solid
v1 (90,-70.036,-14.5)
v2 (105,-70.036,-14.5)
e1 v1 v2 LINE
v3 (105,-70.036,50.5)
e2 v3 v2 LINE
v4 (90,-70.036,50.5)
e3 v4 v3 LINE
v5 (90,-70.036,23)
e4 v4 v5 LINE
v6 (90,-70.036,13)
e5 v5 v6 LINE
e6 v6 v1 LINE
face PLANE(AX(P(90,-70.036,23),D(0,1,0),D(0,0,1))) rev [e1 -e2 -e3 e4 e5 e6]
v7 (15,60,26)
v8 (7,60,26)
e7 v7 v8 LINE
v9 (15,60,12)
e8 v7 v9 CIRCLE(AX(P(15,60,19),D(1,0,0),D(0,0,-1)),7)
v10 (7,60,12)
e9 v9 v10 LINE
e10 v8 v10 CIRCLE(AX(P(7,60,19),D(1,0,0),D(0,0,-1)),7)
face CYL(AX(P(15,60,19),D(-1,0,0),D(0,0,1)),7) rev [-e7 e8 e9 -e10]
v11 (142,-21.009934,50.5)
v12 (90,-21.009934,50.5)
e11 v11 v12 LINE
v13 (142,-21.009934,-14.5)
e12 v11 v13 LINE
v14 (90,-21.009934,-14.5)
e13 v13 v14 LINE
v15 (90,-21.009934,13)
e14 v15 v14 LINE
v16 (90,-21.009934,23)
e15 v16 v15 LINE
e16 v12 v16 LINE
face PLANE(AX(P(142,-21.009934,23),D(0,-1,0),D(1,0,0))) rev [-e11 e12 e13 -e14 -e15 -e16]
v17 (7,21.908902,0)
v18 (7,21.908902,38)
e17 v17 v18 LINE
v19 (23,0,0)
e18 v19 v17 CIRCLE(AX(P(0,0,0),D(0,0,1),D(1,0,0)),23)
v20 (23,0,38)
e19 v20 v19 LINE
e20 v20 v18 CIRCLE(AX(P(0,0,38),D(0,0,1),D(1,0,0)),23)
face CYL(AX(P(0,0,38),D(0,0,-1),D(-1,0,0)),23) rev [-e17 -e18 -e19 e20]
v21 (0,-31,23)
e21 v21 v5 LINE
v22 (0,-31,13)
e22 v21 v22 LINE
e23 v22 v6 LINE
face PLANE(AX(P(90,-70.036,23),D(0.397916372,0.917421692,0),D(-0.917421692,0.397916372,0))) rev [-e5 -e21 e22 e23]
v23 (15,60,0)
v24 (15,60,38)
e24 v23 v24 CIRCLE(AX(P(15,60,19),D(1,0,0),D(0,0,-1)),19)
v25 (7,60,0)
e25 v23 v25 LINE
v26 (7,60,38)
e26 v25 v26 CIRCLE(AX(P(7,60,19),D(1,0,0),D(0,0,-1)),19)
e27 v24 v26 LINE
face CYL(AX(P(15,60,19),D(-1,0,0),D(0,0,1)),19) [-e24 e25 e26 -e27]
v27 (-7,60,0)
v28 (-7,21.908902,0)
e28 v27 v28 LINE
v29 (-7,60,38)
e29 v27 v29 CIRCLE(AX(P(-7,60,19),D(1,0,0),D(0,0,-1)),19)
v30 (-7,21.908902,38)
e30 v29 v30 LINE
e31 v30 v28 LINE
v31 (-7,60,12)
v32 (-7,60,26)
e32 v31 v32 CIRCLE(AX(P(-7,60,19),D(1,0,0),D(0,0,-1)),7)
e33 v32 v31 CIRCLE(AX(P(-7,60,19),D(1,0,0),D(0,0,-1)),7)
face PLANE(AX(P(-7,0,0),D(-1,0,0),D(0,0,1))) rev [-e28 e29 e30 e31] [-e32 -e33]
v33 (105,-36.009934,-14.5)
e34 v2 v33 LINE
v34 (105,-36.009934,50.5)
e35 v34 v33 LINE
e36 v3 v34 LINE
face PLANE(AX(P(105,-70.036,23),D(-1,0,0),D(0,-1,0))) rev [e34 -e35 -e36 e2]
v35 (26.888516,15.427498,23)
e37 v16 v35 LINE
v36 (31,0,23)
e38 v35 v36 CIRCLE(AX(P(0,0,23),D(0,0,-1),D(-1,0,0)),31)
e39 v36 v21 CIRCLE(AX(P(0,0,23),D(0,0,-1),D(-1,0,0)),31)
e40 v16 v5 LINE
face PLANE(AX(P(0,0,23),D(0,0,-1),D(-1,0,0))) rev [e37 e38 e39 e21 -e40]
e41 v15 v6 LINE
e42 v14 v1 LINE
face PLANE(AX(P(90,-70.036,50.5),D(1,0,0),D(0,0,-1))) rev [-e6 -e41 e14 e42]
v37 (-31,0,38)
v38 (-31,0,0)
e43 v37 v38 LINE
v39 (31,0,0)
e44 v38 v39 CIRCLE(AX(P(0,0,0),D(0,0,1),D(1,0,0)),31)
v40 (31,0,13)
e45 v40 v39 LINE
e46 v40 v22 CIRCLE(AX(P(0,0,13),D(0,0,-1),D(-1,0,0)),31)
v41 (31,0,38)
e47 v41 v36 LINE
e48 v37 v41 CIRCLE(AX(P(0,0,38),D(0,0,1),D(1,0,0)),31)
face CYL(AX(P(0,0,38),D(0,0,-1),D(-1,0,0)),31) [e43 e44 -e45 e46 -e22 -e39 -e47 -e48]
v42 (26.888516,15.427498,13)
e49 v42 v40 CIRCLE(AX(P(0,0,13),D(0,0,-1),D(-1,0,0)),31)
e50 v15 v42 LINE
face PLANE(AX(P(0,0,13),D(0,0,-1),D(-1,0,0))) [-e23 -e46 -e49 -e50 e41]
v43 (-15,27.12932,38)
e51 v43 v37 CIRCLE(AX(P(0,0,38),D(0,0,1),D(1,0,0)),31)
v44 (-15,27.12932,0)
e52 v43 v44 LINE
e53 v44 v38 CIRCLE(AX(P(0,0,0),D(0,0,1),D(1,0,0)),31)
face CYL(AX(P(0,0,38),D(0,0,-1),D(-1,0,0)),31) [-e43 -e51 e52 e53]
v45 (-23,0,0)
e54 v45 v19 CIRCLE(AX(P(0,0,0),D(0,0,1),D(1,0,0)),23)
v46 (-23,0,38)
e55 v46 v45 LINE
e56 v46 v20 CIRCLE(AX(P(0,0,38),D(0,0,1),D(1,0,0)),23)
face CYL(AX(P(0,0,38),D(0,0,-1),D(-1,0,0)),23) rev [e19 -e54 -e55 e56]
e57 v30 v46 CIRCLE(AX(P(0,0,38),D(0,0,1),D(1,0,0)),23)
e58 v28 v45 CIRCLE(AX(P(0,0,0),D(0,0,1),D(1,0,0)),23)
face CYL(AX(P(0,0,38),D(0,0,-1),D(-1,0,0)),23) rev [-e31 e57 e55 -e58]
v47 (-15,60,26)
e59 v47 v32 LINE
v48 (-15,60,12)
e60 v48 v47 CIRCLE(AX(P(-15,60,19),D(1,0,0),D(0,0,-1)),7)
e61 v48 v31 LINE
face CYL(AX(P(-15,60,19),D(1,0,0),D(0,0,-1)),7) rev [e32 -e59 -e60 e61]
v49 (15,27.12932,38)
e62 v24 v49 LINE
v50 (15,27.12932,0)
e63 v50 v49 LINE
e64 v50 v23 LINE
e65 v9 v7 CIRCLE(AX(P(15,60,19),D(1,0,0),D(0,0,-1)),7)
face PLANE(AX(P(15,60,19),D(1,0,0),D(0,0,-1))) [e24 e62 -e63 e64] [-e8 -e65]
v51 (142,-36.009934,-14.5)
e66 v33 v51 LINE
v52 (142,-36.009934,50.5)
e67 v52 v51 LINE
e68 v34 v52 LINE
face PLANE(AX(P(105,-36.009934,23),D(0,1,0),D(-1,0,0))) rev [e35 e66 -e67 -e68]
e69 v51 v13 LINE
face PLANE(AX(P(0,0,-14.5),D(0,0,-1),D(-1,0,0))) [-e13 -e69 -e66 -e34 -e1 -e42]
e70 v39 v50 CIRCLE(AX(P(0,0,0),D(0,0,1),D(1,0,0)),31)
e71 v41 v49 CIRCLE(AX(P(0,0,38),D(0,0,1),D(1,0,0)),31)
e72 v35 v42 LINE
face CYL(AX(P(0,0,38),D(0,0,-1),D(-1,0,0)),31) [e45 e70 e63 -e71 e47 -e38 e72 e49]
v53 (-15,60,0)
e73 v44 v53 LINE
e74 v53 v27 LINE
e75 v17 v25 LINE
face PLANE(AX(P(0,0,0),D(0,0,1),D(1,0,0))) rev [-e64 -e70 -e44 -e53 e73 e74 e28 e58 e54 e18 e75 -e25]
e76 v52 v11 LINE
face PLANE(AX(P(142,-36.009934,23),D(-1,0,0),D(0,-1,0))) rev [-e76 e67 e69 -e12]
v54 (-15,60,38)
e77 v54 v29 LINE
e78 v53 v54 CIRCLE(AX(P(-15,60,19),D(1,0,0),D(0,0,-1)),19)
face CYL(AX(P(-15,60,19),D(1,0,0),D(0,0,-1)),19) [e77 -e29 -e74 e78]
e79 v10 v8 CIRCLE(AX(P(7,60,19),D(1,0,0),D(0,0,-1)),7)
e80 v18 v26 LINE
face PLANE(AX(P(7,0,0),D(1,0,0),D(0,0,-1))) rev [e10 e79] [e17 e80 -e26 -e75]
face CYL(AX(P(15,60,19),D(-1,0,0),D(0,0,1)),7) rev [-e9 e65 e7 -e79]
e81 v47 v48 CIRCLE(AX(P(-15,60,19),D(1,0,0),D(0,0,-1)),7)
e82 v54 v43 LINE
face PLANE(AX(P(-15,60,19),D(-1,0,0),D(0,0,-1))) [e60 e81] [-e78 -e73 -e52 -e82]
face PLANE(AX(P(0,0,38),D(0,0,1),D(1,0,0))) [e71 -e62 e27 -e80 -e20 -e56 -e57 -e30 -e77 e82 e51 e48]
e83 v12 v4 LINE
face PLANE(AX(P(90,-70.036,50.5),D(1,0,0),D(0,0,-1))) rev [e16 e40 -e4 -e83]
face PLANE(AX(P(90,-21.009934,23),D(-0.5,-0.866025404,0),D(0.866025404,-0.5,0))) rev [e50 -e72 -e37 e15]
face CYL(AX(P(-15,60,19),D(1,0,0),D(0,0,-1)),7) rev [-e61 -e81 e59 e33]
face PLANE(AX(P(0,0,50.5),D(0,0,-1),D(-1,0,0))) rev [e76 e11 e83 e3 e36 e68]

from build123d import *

# Parameters (mm, degrees)
CLAMP_RING_SKETCH_46_62_R   = 31
CLAMP_RING_SKETCH_46_62_R_2 = 23
CLAMP_RING_62X38_DEPTH      = 38
RING_CUT_DEPTH              = 38
CLEVIS_LUG_SKETCH_R         = 7
CLEVIS_LUG_DEPTH            = 8
ANGLE_BRACKET_DEPTH         = 32.5
SUPPORT_WEB_DEPTH           = 5


with BuildPart() as part:
    # Clamp Ring Sketch Ø46-Ø62 → Clamp Ring Ø62x38 (new body)
    with BuildSketch(Plane.XY):
        Circle(CLAMP_RING_SKETCH_46_62_R)
        Circle(CLAMP_RING_SKETCH_46_62_R_2, mode=Mode.SUBTRACT)
    extrude(amount=CLAMP_RING_62X38_DEPTH)

    # Ring Cut Sketch → Ring Cut (cut)
    with BuildSketch(Plane.XY.offset(38)):
        Polygon((0, 0), (-7, 0), (-7, 40.569348476), (7, 40.569348476), (7, 0), align=None)
    extrude(amount=-RING_CUT_DEPTH, mode=Mode.SUBTRACT)

    # Clevis Lug Sketch → Clevis Lug (add)
    with BuildSketch(Plane(origin=(7, 0, 0), x_dir=(0, 0, -1), z_dir=(1, 0, 0))):
        with BuildLine():
            Line((-38, 60), (-38, 21.9089023))
            Line((-38, 21.9089023), (0, 21.9089023))
            Line((0, 21.9089023), (0, 60))
            ThreePointArc((0, 60), (-19, 79), (-38, 60))
        make_face()
        with Locations((-19, 60)):
            Circle(CLEVIS_LUG_SKETCH_R, mode=Mode.SUBTRACT)
    clevis_lug = extrude(amount=CLEVIS_LUG_DEPTH)

    # Clevis Lug Mirror: Clevis Lug across plane
    add(clevis_lug.mirror(Plane(origin=(0, 0, 0), x_dir=(0, 0, 1), z_dir=(1, 0, 0))))



with BuildPart() as body_2:
    # Angle Bracket Sketch → Angle Bracket (new, symmetric)
    with BuildSketch(Plane.XY.offset(18)):
        Polygon((90, -70.036000309), (105, -70.036000309), (105, -36.009933812), (142, -36.009933812), (142, -21.009933812), (90, -21.009933812), align=None)
    extrude(amount=ANGLE_BRACKET_DEPTH, both=True)


with BuildPart() as part_1:
    add(part.part)

    add(body_2.part)  # Support Web merges body 2
    # Support Web Sketch 60deg → Support Web (add, symmetric)
    with BuildSketch(Plane.XY.offset(18)):
        with BuildLine():
            Line((90, -70.036000309), (0, -31))
            ThreePointArc((0, -31), (26.825849969, -15.536208463), (26.888515957, 15.427498489))
            Line((26.888515957, 15.427498489), (90, -21.009933812))
            Line((90, -21.009933812), (142, -21.009933812))
            Line((142, -21.009933812), (142, -36.009933812))
            Line((142, -36.009933812), (105, -36.009933812))
            Line((105, -36.009933812), (105, -70.036000309))
            Line((105, -70.036000309), (90, -70.036000309))
        make_face()
    extrude(amount=SUPPORT_WEB_DEPTH, both=True)


solid = part_1.part
